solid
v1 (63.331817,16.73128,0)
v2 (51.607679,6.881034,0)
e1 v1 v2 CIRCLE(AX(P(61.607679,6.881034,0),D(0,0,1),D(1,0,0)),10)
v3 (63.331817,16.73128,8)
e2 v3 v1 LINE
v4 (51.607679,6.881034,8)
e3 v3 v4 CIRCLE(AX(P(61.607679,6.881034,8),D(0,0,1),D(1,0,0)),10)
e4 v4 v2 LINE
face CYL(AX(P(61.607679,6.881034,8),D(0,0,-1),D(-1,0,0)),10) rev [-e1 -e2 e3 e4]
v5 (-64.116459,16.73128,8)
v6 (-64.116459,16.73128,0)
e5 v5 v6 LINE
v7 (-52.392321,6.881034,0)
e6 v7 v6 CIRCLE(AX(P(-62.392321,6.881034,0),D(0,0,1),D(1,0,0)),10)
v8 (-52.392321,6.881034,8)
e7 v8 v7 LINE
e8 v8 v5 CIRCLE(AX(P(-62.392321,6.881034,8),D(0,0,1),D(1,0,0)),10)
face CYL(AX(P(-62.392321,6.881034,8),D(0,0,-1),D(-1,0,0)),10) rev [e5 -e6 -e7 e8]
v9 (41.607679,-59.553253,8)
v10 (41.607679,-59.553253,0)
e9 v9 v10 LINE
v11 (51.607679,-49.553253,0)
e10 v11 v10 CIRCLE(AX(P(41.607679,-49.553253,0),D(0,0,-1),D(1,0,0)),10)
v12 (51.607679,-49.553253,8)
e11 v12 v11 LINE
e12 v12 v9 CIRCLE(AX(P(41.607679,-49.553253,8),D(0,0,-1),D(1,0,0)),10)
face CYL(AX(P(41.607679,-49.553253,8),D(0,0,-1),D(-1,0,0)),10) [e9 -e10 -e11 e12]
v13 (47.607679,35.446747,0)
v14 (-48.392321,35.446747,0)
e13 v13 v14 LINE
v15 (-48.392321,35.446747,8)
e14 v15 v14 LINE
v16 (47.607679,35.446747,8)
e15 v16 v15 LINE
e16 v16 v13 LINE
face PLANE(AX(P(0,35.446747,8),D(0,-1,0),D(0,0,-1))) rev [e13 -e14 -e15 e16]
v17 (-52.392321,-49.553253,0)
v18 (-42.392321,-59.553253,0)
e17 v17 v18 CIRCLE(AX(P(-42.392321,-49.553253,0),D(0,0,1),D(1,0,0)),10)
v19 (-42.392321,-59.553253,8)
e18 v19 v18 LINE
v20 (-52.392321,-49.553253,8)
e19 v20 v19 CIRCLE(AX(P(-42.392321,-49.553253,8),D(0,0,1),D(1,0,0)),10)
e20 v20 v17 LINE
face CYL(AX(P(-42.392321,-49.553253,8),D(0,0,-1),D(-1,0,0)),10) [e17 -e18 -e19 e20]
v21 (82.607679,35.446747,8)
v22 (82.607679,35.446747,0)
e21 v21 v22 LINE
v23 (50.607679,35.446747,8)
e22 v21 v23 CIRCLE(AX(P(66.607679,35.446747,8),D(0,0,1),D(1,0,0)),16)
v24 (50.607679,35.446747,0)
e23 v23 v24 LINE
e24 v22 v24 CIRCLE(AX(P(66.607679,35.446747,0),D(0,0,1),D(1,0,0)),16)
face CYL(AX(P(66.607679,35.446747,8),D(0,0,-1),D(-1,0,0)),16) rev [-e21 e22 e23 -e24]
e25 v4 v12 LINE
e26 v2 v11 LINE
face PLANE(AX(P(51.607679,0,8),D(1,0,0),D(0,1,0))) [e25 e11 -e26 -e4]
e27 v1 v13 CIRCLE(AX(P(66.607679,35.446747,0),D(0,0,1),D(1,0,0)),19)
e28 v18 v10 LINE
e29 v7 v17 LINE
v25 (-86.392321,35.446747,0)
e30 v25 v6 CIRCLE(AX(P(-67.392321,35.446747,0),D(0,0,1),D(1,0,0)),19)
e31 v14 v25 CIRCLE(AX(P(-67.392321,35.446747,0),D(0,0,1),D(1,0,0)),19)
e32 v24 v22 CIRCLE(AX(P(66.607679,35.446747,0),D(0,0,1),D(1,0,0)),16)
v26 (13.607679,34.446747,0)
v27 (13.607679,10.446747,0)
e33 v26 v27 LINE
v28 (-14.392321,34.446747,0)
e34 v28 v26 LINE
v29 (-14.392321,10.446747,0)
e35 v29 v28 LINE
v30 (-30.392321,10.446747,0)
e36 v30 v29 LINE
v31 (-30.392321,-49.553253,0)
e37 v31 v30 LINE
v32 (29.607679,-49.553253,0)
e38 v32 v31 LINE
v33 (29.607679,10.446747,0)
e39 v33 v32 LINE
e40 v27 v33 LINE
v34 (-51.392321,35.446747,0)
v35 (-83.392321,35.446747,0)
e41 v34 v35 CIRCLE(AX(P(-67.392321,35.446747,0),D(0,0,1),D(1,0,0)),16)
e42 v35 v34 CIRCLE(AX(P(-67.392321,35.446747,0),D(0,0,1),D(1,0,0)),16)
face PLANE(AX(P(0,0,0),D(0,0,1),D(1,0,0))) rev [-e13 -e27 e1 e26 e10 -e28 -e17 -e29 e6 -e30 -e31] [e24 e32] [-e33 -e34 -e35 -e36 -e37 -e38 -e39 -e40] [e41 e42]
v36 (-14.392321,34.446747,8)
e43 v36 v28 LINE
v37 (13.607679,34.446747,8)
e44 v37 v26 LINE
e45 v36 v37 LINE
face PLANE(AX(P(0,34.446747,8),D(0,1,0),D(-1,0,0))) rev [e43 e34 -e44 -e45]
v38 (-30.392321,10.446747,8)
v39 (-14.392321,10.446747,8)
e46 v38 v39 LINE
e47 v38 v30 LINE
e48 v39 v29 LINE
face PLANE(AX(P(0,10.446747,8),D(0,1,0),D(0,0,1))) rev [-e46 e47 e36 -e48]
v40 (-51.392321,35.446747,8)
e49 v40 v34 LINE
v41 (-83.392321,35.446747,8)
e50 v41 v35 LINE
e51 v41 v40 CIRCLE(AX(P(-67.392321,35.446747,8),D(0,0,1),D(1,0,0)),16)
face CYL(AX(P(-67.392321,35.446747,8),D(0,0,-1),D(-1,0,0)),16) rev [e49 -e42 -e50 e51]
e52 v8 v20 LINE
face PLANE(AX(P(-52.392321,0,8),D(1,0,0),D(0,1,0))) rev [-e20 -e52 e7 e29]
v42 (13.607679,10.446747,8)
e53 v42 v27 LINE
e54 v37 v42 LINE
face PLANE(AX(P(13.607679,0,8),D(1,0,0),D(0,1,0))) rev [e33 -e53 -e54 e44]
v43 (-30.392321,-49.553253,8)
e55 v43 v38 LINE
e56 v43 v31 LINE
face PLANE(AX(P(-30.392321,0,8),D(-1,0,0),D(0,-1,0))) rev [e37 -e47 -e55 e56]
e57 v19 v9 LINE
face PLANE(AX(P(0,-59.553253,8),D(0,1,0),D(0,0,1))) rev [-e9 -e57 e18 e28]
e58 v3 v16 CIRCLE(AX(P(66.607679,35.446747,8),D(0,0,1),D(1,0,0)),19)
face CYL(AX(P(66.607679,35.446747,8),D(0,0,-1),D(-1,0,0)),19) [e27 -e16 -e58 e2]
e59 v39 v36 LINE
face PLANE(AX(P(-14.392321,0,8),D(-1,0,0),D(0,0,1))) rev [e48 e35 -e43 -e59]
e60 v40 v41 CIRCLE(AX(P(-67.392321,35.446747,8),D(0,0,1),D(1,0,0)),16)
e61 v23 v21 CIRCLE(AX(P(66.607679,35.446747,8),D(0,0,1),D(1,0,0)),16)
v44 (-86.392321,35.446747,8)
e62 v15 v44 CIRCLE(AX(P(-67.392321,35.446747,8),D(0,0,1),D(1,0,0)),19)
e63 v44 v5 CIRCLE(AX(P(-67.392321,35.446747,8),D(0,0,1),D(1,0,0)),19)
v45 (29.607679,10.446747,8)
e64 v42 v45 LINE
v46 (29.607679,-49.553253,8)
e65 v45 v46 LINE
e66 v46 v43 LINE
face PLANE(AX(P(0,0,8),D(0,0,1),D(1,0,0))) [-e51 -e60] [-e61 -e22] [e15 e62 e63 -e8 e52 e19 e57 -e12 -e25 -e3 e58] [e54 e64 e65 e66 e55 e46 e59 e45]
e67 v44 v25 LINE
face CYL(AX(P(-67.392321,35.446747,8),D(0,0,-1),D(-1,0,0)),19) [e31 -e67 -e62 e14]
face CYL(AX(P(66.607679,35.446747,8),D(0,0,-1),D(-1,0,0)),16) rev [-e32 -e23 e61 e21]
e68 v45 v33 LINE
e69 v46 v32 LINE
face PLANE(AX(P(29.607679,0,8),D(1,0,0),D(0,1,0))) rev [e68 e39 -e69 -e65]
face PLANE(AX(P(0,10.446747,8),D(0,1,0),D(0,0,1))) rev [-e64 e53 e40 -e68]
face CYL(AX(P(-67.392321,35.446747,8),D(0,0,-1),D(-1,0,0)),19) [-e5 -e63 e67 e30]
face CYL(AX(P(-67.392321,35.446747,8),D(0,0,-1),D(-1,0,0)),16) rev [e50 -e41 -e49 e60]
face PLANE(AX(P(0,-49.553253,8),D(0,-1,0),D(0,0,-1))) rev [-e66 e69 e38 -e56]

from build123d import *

# Parameters (mm, degrees)
SKETCH_1_R      = 16
EXTRUDE_1_DEPTH = 8


with BuildPart() as part:
    # 草图1 → 凸台-拉伸1 (new body)
    with BuildSketch(Plane.XY):
        with BuildLine():
            ThreePointArc((63.331817296, 16.731279855), (81.154867742, 47.668830358), (47.607679365, 35.446747461))
            Line((47.607679365, 35.446747461), (-47.607679365, 35.446747461))
            Line((-47.607679365, 35.446747461), (-48.392320635, 35.446747461))
            ThreePointArc((-48.392320635, 35.446747461), (-81.939509011, 47.668830358), (-64.116458566, 16.731279855))
            ThreePointArc((-64.116458566, 16.731279855), (-55.959645426, 14.537448682), (-52.392320635, 6.881033747))
            Line((-52.392320635, 6.881033747), (-52.392320635, -49.553252539))
            ThreePointArc((-52.392320635, -49.553252539), (-49.463388447, -56.624320351), (-42.392320635, -59.553252539))
            Line((-42.392320635, -59.553252539), (41.607679365, -59.553252539))
            ThreePointArc((41.607679365, -59.553252539), (48.678747177, -56.624320351), (51.607679365, -49.553252539))
            Line((51.607679365, -49.553252539), (51.607679365, 6.881033747))
            ThreePointArc((51.607679365, 6.881033747), (55.175004156, 14.537448682), (63.331817296, 16.731279855))
        make_face()
        Polygon((19.522836201, -49.553252539), (-28.363655741, -49.553252539), (-30.392320635, -49.553252539), (-30.392320635, 10.446747461), (-14.392320635, 10.446747461), (-14.392320635, 34.446747461), (13.607679365, 34.446747461), (13.607679365, 10.446747461), (29.607679365, 10.446747461), (29.607679365, -49.553252539), align=None, mode=Mode.SUBTRACT)
        with Locations((-67.392320635, 35.446747461)):
            Circle(SKETCH_1_R, mode=Mode.SUBTRACT)
        with Locations((66.607679365, 35.446747461)):
            Circle(SKETCH_1_R, mode=Mode.SUBTRACT)
    extrude(amount=EXTRUDE_1_DEPTH)


solid = part.part
